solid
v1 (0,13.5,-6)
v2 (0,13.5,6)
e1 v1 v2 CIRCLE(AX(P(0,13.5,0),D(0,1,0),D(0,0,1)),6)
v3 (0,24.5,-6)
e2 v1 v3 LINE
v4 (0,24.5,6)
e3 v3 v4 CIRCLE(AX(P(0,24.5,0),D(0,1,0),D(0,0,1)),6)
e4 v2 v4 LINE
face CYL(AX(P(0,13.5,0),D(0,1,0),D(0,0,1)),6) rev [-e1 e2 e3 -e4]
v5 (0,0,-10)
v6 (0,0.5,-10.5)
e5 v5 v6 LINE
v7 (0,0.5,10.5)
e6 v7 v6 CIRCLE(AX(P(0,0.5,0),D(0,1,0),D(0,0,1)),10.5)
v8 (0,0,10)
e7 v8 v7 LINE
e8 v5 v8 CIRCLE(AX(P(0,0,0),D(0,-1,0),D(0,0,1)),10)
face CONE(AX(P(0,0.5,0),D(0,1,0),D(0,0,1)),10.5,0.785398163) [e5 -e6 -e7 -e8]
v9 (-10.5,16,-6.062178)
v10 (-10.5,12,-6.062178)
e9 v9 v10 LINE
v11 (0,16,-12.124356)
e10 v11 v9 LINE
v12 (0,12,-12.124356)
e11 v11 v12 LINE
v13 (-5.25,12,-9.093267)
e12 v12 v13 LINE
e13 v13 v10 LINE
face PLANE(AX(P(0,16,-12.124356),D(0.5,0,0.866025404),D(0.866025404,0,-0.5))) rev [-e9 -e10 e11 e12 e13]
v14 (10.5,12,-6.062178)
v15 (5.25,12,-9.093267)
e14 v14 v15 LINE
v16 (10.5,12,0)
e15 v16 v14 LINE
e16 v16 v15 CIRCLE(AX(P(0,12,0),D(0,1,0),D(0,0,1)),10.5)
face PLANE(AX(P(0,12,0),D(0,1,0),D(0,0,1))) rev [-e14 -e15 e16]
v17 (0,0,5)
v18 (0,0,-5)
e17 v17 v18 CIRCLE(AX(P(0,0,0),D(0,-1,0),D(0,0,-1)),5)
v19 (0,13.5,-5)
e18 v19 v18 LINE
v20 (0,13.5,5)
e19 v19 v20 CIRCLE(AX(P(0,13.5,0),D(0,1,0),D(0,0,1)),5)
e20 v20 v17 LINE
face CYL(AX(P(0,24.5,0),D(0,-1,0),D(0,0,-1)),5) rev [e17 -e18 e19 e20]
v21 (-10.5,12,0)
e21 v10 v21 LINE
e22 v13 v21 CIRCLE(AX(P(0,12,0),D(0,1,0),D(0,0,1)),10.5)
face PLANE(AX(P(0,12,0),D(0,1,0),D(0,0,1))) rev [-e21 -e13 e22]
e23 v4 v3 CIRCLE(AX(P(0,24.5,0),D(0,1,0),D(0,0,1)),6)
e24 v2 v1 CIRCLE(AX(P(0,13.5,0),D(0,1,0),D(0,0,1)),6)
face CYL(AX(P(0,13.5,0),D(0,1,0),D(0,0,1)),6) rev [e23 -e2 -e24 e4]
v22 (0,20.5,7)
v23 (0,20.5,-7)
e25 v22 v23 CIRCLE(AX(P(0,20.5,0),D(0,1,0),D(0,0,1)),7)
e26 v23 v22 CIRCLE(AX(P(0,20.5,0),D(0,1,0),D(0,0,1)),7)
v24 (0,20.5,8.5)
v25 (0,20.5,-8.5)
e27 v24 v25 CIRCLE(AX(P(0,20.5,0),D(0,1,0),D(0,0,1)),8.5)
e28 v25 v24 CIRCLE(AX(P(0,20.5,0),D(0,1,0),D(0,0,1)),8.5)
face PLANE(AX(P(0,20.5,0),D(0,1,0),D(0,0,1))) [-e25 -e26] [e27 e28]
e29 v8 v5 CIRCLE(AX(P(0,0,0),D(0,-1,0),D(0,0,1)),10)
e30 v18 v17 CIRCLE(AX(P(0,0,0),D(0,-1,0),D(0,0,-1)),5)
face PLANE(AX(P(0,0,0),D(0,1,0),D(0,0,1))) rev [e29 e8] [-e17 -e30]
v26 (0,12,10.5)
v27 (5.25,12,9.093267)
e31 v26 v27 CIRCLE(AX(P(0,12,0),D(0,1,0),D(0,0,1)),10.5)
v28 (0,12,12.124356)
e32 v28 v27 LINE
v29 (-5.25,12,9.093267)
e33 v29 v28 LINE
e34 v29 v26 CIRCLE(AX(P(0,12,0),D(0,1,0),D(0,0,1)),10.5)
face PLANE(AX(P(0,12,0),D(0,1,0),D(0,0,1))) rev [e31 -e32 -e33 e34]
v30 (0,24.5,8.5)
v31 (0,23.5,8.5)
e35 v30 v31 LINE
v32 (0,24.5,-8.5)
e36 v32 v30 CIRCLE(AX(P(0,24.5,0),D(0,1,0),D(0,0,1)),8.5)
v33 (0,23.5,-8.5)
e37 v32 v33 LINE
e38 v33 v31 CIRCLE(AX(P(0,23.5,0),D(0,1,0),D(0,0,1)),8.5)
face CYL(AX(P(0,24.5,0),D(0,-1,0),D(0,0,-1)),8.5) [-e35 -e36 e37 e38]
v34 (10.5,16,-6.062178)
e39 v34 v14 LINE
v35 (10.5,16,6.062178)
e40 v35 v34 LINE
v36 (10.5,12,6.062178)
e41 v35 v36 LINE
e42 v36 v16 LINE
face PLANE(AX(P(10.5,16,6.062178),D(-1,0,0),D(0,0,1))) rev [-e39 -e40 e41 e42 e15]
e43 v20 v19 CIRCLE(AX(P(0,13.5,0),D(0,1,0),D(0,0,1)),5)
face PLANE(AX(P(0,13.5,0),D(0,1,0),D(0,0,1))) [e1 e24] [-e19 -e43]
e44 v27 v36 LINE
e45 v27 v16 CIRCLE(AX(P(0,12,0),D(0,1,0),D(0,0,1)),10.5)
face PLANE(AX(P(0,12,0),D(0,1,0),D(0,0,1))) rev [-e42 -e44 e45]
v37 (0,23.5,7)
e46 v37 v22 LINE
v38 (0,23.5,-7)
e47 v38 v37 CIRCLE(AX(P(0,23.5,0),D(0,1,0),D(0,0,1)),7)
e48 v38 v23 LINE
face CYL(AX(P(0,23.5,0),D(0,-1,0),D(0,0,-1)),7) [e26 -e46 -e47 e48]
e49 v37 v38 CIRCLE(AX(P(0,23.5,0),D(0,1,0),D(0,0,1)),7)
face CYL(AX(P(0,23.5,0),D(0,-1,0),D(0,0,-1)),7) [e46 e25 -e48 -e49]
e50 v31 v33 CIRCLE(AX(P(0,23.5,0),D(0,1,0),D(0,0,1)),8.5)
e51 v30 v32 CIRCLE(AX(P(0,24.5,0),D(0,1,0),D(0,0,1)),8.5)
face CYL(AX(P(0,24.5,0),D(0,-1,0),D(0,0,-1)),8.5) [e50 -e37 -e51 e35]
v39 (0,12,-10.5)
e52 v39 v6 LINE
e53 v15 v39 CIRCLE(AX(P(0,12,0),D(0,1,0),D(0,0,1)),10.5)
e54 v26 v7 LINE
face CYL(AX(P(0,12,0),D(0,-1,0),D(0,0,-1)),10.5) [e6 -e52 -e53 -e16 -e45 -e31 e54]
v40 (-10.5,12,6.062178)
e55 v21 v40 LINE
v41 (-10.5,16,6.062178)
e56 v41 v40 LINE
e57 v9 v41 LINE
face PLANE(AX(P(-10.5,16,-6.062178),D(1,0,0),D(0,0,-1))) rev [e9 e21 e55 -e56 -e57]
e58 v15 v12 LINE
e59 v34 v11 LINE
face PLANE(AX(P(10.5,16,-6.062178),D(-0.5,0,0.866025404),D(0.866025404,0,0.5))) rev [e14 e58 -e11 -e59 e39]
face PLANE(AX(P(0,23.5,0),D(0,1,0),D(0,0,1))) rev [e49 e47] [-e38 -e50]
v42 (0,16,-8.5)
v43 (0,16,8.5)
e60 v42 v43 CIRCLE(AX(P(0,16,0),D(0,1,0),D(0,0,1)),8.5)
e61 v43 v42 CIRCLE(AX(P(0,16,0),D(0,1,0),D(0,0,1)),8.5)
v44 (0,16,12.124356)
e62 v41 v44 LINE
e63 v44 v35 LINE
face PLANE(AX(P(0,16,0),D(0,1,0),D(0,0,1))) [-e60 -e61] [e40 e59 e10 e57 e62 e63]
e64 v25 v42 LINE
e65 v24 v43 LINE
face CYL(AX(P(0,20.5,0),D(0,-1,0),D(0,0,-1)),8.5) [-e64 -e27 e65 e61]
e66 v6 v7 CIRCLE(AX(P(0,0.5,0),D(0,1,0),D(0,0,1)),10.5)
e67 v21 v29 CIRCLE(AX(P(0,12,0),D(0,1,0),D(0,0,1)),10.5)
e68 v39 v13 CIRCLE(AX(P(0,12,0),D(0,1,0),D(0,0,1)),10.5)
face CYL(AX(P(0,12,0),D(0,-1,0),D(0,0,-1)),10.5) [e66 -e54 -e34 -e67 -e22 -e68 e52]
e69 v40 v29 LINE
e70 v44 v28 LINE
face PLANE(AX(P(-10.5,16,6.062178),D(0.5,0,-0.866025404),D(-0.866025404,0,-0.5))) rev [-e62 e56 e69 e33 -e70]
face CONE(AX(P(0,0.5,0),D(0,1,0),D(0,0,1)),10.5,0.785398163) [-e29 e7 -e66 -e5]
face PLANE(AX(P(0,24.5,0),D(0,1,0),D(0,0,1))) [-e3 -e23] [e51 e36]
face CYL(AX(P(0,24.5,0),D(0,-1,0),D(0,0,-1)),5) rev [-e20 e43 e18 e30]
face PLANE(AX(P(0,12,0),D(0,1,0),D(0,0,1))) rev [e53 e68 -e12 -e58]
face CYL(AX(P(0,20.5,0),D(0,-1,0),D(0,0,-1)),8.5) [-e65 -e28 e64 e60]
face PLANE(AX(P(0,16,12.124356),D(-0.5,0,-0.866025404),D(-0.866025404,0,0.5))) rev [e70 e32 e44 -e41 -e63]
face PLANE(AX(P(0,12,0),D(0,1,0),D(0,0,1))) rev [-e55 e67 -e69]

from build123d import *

# Parameters (mm, degrees)
SKETCH2_R           = 10.5
BOSS_EXTRUDE1_DEPTH = 12
BOSS_EXTRUDE2_DEPTH = 4
SKETCH4_R           = 8.5
BOSS_EXTRUDE3_DEPTH = 4.5
SKETCH5_R           = 7
BOSS_EXTRUDE4_DEPTH = 3
SKETCH7_R           = 8.5
BOSS_EXTRUDE5_DEPTH = 1
CHAMFER1_SIZE       = 0.5
SKETCH9_R           = 6
CUT_EXTRUDE1_DEPTH  = 11
SKETCH8_R           = 5
CUT_EXTRUDE2_DEPTH  = 30.283100929


with BuildPart() as part:
    # Sketch2 → Boss-Extrude1 (new body)
    with BuildSketch(Plane(origin=(0, 0, 0), x_dir=(1, 0, 0), z_dir=(0, 1, 0))):
        with Locations(Location((0, 0, 0), (0, 0, 270))):
            Circle(SKETCH2_R)
    extrude(amount=BOSS_EXTRUDE1_DEPTH)

    # Sketch3 → Boss-Extrude2 (add)
    with BuildSketch(Plane(origin=(0, 12, 0), x_dir=(1, 0, 0), z_dir=(0, 1, 0))):
        Polygon((10.5, -6.062177826), (10.5, 6.062177826), (0, 12.124355653), (-10.5, 6.062177826), (-10.5, -6.062177826), (0, -12.124355653), align=None)
    extrude(amount=BOSS_EXTRUDE2_DEPTH)

    # Sketch4 → Boss-Extrude3 (add)
    with BuildSketch(Plane(origin=(0, 16, 0), x_dir=(1, 0, 0), z_dir=(0, 1, 0))):
        with Locations(Location((0, 0, 0), (0, 0, 270))):
            Circle(SKETCH4_R)
    extrude(amount=BOSS_EXTRUDE3_DEPTH)

    # Sketch5 → Boss-Extrude4 (add)
    with BuildSketch(Plane(origin=(0, 20.5, 0), x_dir=(1, 0, 0), z_dir=(0, 1, 0))):
        with Locations(Location((0, 0, 0), (0, 0, 270))):
            Circle(SKETCH5_R)
    extrude(amount=BOSS_EXTRUDE4_DEPTH)

    # Sketch7 → Boss-Extrude5 (add)
    with BuildSketch(Plane(origin=(0, 23.5, 0), x_dir=(1, 0, 0), z_dir=(0, 1, 0))):
        with Locations(Location((0, 0, 0), (0, 0, 270))):
            Circle(SKETCH7_R)
    extrude(amount=BOSS_EXTRUDE5_DEPTH)

    # Chamfer1
    chamfer1_edges = [part.edges().sort_by_distance(p)[0] for p in [
        (0, 0, -10.5),
    ]]
    chamfer(chamfer1_edges, length=CHAMFER1_SIZE)

    # Sketch9 → Cut-Extrude1 (cut)
    with BuildSketch(Plane(origin=(0, 24.5, 0), x_dir=(1, 0, 0), z_dir=(0, 1, 0))):
        with Locations(Location((0, 0, 0), (0, 0, 270))):
            Circle(SKETCH9_R)
    extrude(amount=-CUT_EXTRUDE1_DEPTH, mode=Mode.SUBTRACT)

    # Sketch8 → Cut-Extrude2 (cut, through all)
    with BuildSketch(Plane.XZ):
        with Locations(Location((0, 0, 0), (0, 0, 270))):
            Circle(SKETCH8_R)
    extrude(amount=-CUT_EXTRUDE2_DEPTH, mode=Mode.SUBTRACT)


solid = part.part
